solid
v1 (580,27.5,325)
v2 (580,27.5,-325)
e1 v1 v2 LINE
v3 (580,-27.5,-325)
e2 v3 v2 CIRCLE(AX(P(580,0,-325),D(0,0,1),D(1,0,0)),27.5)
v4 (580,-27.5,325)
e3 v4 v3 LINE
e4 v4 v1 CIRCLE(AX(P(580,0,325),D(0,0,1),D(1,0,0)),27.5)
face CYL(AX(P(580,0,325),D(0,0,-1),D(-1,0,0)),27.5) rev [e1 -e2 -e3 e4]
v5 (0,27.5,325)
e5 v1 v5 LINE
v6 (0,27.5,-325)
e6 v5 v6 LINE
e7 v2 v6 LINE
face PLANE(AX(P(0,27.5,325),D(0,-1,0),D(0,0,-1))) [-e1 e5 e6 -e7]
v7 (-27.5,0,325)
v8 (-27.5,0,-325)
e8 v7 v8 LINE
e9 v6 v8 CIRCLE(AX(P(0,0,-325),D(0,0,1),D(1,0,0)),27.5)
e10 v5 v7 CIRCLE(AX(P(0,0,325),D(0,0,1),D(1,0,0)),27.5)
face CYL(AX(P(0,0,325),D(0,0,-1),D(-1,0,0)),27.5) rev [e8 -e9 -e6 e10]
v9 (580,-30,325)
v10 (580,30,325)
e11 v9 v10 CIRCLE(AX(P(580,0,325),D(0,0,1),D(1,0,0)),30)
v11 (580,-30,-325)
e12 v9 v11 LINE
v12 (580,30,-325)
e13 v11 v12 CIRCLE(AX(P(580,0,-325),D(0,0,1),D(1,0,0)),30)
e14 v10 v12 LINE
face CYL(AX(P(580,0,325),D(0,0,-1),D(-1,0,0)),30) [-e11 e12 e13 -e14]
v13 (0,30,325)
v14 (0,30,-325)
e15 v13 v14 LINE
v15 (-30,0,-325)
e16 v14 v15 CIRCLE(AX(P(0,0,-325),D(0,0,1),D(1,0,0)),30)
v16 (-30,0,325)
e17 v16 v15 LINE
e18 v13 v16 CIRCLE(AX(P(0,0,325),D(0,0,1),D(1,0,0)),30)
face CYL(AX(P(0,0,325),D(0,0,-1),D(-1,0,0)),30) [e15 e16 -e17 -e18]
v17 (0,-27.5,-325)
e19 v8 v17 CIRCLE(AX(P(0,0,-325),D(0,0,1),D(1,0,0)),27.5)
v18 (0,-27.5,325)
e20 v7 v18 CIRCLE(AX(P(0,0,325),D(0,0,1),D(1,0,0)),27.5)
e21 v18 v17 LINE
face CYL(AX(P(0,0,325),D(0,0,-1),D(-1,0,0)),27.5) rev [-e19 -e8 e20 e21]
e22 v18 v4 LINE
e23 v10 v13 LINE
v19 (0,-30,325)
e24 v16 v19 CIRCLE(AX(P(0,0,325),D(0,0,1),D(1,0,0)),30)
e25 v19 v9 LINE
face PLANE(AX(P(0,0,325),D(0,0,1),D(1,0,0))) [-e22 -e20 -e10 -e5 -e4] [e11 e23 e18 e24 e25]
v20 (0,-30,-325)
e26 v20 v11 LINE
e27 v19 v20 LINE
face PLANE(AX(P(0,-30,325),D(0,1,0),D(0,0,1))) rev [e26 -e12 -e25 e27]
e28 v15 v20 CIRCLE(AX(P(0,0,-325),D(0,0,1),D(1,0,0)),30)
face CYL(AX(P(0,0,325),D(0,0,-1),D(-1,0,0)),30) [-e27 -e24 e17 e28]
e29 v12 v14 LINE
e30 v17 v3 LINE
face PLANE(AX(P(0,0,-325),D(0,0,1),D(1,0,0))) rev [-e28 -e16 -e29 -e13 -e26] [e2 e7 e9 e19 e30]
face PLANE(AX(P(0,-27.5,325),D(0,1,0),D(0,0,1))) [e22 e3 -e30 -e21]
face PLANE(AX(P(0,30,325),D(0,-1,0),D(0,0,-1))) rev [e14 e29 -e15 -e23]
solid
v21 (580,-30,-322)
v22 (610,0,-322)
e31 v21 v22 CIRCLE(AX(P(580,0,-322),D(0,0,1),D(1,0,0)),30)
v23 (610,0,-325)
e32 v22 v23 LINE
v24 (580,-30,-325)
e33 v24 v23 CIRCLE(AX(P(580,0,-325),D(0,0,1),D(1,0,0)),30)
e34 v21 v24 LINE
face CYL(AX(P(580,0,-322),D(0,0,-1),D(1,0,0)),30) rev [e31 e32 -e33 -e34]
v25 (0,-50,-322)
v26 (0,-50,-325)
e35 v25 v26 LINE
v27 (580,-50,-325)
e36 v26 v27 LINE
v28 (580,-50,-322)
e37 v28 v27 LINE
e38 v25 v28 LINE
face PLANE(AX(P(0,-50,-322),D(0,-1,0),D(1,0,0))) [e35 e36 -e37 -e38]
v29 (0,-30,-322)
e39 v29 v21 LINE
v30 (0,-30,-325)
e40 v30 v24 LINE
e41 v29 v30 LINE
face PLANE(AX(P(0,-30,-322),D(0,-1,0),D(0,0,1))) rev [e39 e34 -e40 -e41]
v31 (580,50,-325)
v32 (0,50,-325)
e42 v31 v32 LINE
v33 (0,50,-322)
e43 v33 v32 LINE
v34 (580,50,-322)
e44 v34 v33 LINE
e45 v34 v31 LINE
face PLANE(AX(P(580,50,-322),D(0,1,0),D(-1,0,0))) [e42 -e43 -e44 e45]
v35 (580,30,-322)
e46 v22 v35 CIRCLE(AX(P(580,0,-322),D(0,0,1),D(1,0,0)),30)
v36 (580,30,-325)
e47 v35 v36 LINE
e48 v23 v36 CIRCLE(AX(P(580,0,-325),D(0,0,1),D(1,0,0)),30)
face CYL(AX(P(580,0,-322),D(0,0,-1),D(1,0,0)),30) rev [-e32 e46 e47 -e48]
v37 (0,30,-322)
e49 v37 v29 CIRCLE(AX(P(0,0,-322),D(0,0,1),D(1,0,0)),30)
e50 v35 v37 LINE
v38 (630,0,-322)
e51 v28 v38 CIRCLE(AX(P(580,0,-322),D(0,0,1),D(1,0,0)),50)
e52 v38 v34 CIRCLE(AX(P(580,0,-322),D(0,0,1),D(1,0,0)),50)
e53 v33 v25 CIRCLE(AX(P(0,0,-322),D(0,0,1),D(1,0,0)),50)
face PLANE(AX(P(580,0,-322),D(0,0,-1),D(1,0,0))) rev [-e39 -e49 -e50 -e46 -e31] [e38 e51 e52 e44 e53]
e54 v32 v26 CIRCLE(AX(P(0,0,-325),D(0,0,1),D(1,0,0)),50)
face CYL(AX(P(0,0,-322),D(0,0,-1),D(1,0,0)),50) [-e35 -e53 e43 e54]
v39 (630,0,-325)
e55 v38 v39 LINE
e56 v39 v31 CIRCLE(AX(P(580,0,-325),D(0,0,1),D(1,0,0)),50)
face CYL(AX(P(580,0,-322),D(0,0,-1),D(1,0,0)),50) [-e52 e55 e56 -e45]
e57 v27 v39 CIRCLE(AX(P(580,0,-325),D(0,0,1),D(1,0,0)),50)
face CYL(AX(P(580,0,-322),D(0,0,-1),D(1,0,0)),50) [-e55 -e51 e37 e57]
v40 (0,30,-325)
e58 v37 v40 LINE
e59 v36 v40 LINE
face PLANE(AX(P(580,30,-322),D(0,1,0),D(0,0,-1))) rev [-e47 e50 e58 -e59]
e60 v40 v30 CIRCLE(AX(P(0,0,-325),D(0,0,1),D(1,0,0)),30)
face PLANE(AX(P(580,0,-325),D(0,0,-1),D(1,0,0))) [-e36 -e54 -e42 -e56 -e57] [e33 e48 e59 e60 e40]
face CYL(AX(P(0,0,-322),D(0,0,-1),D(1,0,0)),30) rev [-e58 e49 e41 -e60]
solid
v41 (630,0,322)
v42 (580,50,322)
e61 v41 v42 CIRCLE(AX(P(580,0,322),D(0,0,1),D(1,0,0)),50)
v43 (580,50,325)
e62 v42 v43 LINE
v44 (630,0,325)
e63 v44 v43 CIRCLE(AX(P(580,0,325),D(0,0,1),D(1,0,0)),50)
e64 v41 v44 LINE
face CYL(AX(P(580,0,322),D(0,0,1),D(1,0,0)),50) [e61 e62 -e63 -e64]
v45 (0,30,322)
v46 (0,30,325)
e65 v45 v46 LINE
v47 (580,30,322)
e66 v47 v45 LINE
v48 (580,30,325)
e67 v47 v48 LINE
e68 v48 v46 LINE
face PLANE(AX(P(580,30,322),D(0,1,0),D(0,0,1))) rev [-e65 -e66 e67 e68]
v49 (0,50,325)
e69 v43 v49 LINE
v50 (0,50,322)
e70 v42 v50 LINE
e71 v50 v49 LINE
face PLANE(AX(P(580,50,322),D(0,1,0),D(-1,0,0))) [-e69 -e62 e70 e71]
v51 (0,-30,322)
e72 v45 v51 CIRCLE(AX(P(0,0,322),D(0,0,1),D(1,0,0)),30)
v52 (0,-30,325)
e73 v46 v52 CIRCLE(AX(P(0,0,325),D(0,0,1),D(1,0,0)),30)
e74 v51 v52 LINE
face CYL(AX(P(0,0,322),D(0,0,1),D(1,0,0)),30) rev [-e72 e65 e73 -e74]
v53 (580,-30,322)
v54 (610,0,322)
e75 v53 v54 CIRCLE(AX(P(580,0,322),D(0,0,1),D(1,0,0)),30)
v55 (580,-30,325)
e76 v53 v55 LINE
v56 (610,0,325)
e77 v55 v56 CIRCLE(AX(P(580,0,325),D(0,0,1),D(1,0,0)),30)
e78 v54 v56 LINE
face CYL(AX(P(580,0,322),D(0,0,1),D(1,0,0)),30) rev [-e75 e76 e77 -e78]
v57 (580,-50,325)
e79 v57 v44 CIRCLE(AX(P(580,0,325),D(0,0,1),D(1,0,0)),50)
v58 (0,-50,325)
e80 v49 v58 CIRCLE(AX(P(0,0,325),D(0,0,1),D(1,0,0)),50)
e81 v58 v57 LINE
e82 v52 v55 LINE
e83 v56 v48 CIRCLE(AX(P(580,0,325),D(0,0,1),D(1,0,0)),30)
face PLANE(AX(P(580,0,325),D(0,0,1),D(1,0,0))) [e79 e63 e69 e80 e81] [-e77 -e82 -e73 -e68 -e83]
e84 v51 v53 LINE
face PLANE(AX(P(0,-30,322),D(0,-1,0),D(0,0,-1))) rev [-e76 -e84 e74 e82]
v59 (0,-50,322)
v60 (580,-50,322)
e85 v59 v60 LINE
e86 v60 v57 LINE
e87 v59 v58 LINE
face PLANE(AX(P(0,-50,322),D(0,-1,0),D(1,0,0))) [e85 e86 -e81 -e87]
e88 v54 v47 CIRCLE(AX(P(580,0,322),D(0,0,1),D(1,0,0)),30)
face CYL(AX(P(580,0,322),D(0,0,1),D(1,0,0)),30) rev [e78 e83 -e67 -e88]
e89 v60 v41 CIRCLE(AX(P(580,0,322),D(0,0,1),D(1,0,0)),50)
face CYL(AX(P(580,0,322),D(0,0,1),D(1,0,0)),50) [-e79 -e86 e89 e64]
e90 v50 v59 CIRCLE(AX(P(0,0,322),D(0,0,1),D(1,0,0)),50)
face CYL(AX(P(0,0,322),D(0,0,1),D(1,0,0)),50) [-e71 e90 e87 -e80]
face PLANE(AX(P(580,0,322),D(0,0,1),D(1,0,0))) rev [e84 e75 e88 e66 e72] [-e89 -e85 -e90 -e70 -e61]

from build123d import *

# Parameters (mm, degrees)
BOSS_EXTRUDE1_DEPTH = 325
BOSS_EXTRUDE2_DEPTH = 3


with BuildPart() as part:
    # Sketch1 → Boss-Extrude1 (new, symmetric)
    with BuildSketch(Plane.XY):
        with BuildLine():
            Line((0, 30), (580, 30))
            ThreePointArc((580, 30), (610, 0), (580, -30))
            Line((580, -30), (0, -30))
            ThreePointArc((0, -30), (-30, 0), (0, 30))
        make_face()
        with BuildLine():
            Line((0, 27.5), (580, 27.5))
            ThreePointArc((580, 27.5), (607.5, 0), (580, -27.5))
            Line((580, -27.5), (0, -27.5))
            ThreePointArc((0, -27.5), (-27.5, 0), (0, 27.5))
        make_face(mode=Mode.SUBTRACT)
    extrude(amount=BOSS_EXTRUDE1_DEPTH, both=True)


with BuildPart() as body_2:
    # Sketch2 → Boss-Extrude2 (new body)
    with BuildSketch(Plane.XY.offset(325)):
        with BuildLine():
            Line((580, 50), (0, 50))
            ThreePointArc((0, 50), (-50, 0), (0, -50))
            Line((0, -50), (580, -50))
            ThreePointArc((580, -50), (630, 0), (580, 50))
        make_face()
        with BuildLine():
            Line((0, -30), (580, -30))
            ThreePointArc((580, -30), (610, 0), (580, 30))
            Line((580, 30), (0, 30))
            ThreePointArc((0, 30), (-30, 0), (0, -30))
        make_face(mode=Mode.SUBTRACT)
    extrude(amount=-BOSS_EXTRUDE2_DEPTH)


with BuildPart() as body_3:
    # Mirror1: mirrored copy
    add(body_2.part.mirror(Plane.XY))


solid = Compound([part.part, body_2.part, body_3.part])
